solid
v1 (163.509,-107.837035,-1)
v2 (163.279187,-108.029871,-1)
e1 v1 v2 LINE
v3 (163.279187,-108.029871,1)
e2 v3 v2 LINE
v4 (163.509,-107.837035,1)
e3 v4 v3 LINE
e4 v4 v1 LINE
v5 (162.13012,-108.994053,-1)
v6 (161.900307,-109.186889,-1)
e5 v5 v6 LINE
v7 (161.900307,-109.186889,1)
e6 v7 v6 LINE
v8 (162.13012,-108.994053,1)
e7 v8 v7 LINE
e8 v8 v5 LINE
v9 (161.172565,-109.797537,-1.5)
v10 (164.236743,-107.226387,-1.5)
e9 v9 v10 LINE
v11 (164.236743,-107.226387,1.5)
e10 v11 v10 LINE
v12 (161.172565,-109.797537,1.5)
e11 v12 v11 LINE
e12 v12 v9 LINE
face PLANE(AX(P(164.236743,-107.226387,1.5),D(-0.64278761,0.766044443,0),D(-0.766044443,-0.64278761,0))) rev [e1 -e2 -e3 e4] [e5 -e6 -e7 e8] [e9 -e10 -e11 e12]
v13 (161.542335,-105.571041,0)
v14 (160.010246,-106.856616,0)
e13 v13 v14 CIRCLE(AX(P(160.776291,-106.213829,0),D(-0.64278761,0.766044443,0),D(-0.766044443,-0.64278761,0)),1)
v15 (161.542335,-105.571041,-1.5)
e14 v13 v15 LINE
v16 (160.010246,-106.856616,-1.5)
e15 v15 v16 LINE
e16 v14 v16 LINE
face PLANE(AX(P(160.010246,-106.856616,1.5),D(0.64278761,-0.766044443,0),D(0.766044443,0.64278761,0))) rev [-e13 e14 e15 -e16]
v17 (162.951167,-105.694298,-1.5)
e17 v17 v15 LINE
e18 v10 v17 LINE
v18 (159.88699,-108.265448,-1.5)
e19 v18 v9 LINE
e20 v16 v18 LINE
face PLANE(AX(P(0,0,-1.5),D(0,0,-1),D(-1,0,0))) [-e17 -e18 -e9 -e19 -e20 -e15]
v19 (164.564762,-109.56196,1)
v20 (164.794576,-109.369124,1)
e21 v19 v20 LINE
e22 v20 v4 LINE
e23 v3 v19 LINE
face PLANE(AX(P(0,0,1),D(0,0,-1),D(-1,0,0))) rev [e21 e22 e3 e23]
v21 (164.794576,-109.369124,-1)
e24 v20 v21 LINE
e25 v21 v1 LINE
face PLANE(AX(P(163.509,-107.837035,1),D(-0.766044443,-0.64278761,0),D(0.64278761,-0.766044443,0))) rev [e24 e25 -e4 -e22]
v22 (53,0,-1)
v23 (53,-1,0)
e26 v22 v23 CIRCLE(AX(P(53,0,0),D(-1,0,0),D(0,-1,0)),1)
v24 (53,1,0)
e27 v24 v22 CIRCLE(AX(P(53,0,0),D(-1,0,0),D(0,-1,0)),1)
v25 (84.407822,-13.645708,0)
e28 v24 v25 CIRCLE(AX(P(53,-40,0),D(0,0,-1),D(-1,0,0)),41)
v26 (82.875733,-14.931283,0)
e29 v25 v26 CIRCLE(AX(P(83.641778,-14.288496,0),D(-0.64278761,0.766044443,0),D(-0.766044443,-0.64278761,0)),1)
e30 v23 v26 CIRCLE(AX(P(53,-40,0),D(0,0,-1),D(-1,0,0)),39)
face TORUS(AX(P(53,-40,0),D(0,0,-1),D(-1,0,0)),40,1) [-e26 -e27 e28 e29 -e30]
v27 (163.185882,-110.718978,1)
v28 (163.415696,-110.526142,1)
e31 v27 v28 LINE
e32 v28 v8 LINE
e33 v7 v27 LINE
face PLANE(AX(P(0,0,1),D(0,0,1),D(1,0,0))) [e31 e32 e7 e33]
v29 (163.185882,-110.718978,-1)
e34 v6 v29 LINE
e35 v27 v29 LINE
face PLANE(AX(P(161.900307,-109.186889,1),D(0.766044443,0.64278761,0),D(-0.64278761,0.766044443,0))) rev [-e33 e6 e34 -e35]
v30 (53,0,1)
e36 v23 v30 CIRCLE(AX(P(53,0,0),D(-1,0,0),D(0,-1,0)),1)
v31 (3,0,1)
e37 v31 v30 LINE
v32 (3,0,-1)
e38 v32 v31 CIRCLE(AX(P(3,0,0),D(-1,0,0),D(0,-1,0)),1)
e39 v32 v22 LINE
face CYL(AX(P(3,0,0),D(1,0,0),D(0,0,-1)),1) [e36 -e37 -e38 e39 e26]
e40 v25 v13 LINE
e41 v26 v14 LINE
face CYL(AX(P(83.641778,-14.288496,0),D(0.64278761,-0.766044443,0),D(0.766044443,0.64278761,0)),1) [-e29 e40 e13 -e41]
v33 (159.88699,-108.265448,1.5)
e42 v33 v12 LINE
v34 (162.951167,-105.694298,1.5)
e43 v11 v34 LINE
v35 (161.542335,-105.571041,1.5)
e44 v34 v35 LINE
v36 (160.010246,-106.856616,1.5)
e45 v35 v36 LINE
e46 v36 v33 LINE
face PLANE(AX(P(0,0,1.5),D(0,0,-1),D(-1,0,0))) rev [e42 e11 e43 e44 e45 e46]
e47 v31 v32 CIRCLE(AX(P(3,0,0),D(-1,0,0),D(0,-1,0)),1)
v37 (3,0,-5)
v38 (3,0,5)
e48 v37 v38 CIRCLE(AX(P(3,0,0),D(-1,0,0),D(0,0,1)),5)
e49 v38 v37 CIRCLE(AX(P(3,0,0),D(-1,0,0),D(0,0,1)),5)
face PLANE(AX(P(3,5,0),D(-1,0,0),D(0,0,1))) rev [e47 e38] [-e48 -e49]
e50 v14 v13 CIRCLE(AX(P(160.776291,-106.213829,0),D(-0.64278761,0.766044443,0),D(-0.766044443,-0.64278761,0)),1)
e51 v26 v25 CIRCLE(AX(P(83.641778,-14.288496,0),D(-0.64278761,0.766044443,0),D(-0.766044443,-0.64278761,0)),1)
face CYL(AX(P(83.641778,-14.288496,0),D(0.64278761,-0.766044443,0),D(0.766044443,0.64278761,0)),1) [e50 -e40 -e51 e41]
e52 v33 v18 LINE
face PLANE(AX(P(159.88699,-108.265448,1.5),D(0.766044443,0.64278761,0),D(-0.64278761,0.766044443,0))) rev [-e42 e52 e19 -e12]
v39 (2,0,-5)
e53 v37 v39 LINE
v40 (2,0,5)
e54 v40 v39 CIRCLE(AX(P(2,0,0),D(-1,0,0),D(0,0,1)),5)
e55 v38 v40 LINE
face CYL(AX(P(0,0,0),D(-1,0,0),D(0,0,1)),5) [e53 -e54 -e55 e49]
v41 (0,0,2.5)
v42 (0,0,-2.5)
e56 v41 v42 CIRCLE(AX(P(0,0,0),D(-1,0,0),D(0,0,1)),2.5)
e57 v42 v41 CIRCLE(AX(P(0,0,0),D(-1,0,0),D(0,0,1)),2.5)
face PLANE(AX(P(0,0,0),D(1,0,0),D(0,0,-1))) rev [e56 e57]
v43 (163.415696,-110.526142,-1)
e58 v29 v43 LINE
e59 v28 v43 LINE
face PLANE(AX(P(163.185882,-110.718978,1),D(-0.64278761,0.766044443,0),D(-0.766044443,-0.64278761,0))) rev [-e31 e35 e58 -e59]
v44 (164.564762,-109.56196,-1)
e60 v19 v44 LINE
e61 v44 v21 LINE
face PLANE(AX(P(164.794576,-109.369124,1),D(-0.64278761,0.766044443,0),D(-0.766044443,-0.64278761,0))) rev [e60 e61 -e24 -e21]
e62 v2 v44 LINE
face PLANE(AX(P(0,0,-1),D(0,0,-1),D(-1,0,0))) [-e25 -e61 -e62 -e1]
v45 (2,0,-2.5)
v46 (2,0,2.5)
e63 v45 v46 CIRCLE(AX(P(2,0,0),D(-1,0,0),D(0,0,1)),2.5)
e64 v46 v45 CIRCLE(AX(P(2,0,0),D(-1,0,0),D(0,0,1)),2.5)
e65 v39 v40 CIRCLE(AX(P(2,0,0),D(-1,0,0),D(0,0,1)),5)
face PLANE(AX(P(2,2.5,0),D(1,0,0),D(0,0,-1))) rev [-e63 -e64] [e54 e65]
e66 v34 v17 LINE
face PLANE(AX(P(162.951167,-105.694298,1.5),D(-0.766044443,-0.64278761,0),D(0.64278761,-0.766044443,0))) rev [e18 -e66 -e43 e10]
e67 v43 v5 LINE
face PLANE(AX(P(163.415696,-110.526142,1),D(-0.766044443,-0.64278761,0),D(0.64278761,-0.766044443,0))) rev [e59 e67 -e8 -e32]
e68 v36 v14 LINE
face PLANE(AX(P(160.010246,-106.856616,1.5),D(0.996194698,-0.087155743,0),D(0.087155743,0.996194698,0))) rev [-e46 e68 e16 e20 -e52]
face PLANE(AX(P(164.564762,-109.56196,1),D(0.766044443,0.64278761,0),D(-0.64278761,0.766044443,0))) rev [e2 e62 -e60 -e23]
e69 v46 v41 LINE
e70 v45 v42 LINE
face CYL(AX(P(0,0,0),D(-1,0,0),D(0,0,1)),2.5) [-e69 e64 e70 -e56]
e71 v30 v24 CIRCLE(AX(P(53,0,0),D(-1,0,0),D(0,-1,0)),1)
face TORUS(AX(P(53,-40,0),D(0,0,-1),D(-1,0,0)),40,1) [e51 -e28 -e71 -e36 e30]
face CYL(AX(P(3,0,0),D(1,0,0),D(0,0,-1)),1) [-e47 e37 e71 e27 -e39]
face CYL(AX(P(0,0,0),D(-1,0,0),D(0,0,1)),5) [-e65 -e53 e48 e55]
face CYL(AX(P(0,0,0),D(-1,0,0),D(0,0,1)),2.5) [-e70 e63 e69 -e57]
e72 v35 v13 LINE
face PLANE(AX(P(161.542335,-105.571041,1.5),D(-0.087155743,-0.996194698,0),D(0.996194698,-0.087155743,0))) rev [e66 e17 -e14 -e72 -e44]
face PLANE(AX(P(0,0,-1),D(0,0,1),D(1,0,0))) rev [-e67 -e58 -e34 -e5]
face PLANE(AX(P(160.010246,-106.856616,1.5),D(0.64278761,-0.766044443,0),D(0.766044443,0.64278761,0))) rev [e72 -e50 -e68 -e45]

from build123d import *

# Parameters (mm, degrees)
SWEEP1_PROFILE_R    = 1
BOSS_EXTRUDE1_DEPTH = 1.5
BOSS_EXTRUDE2_DEPTH = 1


with BuildPart() as part:
    # Sketch1 → Revolve1 (revolve)
    with BuildSketch(Plane.XY, mode=Mode.PRIVATE) as revolve1_sk:
        Polygon((0, 0), (0, 2.5), (2, 2.5), (2, 5), (3, 5), (3, 0), align=None)
    revolve(revolve1_sk.sketch.rotate(Axis((0, 0, 0), (1, 0, 0)), 90), axis=Axis((0, 0, 0), (1, 0, 0)))

    # Sweep1: sweep along a path in Sketch2
    with BuildLine(Plane.XY) as sweep1_path:
        Line((3, 0), (53, 0))
        ThreePointArc((53, 0), (69.90473047, -3.747688519), (83.641777725, -14.288495613))
        Line((83.641777725, -14.288495613), (160.776290887, -106.213828787))
    # Sweep1 profile (on start of the path) → Sweep1 (sweep)
    with BuildSketch(Plane(origin=(3, 0, 0), x_dir=(0, 0, 1), z_dir=(1, 0, 0))):
        Circle(SWEEP1_PROFILE_R)
    sweep(path=sweep1_path.line)

    # Sketch11 → Boss-Extrude1 (add, symmetric)
    with BuildSketch(Plane.XY):
        Polygon((160.010246444, -106.856616397), (161.54233533, -105.571041177), (162.951167383, -105.694298011), (164.236742602, -107.226386897), (161.17256483, -109.797537336), (159.886989611, -108.265448449), align=None)
    extrude(amount=BOSS_EXTRUDE1_DEPTH, both=True)

    # Sketch12 → Boss-Extrude2 (add, symmetric)
    with BuildSketch(Plane.XY):
        Polygon((163.509000381, -107.837035126), (164.794575601, -109.369124012), (164.564762268, -109.561960295), (163.279187049, -108.029871409), align=None)
        Polygon((162.130120384, -108.994052823), (161.900307051, -109.186889106), (163.18588227, -110.718977993), (163.415695603, -110.52614171), align=None)
    extrude(amount=BOSS_EXTRUDE2_DEPTH, both=True)


solid = part.part
